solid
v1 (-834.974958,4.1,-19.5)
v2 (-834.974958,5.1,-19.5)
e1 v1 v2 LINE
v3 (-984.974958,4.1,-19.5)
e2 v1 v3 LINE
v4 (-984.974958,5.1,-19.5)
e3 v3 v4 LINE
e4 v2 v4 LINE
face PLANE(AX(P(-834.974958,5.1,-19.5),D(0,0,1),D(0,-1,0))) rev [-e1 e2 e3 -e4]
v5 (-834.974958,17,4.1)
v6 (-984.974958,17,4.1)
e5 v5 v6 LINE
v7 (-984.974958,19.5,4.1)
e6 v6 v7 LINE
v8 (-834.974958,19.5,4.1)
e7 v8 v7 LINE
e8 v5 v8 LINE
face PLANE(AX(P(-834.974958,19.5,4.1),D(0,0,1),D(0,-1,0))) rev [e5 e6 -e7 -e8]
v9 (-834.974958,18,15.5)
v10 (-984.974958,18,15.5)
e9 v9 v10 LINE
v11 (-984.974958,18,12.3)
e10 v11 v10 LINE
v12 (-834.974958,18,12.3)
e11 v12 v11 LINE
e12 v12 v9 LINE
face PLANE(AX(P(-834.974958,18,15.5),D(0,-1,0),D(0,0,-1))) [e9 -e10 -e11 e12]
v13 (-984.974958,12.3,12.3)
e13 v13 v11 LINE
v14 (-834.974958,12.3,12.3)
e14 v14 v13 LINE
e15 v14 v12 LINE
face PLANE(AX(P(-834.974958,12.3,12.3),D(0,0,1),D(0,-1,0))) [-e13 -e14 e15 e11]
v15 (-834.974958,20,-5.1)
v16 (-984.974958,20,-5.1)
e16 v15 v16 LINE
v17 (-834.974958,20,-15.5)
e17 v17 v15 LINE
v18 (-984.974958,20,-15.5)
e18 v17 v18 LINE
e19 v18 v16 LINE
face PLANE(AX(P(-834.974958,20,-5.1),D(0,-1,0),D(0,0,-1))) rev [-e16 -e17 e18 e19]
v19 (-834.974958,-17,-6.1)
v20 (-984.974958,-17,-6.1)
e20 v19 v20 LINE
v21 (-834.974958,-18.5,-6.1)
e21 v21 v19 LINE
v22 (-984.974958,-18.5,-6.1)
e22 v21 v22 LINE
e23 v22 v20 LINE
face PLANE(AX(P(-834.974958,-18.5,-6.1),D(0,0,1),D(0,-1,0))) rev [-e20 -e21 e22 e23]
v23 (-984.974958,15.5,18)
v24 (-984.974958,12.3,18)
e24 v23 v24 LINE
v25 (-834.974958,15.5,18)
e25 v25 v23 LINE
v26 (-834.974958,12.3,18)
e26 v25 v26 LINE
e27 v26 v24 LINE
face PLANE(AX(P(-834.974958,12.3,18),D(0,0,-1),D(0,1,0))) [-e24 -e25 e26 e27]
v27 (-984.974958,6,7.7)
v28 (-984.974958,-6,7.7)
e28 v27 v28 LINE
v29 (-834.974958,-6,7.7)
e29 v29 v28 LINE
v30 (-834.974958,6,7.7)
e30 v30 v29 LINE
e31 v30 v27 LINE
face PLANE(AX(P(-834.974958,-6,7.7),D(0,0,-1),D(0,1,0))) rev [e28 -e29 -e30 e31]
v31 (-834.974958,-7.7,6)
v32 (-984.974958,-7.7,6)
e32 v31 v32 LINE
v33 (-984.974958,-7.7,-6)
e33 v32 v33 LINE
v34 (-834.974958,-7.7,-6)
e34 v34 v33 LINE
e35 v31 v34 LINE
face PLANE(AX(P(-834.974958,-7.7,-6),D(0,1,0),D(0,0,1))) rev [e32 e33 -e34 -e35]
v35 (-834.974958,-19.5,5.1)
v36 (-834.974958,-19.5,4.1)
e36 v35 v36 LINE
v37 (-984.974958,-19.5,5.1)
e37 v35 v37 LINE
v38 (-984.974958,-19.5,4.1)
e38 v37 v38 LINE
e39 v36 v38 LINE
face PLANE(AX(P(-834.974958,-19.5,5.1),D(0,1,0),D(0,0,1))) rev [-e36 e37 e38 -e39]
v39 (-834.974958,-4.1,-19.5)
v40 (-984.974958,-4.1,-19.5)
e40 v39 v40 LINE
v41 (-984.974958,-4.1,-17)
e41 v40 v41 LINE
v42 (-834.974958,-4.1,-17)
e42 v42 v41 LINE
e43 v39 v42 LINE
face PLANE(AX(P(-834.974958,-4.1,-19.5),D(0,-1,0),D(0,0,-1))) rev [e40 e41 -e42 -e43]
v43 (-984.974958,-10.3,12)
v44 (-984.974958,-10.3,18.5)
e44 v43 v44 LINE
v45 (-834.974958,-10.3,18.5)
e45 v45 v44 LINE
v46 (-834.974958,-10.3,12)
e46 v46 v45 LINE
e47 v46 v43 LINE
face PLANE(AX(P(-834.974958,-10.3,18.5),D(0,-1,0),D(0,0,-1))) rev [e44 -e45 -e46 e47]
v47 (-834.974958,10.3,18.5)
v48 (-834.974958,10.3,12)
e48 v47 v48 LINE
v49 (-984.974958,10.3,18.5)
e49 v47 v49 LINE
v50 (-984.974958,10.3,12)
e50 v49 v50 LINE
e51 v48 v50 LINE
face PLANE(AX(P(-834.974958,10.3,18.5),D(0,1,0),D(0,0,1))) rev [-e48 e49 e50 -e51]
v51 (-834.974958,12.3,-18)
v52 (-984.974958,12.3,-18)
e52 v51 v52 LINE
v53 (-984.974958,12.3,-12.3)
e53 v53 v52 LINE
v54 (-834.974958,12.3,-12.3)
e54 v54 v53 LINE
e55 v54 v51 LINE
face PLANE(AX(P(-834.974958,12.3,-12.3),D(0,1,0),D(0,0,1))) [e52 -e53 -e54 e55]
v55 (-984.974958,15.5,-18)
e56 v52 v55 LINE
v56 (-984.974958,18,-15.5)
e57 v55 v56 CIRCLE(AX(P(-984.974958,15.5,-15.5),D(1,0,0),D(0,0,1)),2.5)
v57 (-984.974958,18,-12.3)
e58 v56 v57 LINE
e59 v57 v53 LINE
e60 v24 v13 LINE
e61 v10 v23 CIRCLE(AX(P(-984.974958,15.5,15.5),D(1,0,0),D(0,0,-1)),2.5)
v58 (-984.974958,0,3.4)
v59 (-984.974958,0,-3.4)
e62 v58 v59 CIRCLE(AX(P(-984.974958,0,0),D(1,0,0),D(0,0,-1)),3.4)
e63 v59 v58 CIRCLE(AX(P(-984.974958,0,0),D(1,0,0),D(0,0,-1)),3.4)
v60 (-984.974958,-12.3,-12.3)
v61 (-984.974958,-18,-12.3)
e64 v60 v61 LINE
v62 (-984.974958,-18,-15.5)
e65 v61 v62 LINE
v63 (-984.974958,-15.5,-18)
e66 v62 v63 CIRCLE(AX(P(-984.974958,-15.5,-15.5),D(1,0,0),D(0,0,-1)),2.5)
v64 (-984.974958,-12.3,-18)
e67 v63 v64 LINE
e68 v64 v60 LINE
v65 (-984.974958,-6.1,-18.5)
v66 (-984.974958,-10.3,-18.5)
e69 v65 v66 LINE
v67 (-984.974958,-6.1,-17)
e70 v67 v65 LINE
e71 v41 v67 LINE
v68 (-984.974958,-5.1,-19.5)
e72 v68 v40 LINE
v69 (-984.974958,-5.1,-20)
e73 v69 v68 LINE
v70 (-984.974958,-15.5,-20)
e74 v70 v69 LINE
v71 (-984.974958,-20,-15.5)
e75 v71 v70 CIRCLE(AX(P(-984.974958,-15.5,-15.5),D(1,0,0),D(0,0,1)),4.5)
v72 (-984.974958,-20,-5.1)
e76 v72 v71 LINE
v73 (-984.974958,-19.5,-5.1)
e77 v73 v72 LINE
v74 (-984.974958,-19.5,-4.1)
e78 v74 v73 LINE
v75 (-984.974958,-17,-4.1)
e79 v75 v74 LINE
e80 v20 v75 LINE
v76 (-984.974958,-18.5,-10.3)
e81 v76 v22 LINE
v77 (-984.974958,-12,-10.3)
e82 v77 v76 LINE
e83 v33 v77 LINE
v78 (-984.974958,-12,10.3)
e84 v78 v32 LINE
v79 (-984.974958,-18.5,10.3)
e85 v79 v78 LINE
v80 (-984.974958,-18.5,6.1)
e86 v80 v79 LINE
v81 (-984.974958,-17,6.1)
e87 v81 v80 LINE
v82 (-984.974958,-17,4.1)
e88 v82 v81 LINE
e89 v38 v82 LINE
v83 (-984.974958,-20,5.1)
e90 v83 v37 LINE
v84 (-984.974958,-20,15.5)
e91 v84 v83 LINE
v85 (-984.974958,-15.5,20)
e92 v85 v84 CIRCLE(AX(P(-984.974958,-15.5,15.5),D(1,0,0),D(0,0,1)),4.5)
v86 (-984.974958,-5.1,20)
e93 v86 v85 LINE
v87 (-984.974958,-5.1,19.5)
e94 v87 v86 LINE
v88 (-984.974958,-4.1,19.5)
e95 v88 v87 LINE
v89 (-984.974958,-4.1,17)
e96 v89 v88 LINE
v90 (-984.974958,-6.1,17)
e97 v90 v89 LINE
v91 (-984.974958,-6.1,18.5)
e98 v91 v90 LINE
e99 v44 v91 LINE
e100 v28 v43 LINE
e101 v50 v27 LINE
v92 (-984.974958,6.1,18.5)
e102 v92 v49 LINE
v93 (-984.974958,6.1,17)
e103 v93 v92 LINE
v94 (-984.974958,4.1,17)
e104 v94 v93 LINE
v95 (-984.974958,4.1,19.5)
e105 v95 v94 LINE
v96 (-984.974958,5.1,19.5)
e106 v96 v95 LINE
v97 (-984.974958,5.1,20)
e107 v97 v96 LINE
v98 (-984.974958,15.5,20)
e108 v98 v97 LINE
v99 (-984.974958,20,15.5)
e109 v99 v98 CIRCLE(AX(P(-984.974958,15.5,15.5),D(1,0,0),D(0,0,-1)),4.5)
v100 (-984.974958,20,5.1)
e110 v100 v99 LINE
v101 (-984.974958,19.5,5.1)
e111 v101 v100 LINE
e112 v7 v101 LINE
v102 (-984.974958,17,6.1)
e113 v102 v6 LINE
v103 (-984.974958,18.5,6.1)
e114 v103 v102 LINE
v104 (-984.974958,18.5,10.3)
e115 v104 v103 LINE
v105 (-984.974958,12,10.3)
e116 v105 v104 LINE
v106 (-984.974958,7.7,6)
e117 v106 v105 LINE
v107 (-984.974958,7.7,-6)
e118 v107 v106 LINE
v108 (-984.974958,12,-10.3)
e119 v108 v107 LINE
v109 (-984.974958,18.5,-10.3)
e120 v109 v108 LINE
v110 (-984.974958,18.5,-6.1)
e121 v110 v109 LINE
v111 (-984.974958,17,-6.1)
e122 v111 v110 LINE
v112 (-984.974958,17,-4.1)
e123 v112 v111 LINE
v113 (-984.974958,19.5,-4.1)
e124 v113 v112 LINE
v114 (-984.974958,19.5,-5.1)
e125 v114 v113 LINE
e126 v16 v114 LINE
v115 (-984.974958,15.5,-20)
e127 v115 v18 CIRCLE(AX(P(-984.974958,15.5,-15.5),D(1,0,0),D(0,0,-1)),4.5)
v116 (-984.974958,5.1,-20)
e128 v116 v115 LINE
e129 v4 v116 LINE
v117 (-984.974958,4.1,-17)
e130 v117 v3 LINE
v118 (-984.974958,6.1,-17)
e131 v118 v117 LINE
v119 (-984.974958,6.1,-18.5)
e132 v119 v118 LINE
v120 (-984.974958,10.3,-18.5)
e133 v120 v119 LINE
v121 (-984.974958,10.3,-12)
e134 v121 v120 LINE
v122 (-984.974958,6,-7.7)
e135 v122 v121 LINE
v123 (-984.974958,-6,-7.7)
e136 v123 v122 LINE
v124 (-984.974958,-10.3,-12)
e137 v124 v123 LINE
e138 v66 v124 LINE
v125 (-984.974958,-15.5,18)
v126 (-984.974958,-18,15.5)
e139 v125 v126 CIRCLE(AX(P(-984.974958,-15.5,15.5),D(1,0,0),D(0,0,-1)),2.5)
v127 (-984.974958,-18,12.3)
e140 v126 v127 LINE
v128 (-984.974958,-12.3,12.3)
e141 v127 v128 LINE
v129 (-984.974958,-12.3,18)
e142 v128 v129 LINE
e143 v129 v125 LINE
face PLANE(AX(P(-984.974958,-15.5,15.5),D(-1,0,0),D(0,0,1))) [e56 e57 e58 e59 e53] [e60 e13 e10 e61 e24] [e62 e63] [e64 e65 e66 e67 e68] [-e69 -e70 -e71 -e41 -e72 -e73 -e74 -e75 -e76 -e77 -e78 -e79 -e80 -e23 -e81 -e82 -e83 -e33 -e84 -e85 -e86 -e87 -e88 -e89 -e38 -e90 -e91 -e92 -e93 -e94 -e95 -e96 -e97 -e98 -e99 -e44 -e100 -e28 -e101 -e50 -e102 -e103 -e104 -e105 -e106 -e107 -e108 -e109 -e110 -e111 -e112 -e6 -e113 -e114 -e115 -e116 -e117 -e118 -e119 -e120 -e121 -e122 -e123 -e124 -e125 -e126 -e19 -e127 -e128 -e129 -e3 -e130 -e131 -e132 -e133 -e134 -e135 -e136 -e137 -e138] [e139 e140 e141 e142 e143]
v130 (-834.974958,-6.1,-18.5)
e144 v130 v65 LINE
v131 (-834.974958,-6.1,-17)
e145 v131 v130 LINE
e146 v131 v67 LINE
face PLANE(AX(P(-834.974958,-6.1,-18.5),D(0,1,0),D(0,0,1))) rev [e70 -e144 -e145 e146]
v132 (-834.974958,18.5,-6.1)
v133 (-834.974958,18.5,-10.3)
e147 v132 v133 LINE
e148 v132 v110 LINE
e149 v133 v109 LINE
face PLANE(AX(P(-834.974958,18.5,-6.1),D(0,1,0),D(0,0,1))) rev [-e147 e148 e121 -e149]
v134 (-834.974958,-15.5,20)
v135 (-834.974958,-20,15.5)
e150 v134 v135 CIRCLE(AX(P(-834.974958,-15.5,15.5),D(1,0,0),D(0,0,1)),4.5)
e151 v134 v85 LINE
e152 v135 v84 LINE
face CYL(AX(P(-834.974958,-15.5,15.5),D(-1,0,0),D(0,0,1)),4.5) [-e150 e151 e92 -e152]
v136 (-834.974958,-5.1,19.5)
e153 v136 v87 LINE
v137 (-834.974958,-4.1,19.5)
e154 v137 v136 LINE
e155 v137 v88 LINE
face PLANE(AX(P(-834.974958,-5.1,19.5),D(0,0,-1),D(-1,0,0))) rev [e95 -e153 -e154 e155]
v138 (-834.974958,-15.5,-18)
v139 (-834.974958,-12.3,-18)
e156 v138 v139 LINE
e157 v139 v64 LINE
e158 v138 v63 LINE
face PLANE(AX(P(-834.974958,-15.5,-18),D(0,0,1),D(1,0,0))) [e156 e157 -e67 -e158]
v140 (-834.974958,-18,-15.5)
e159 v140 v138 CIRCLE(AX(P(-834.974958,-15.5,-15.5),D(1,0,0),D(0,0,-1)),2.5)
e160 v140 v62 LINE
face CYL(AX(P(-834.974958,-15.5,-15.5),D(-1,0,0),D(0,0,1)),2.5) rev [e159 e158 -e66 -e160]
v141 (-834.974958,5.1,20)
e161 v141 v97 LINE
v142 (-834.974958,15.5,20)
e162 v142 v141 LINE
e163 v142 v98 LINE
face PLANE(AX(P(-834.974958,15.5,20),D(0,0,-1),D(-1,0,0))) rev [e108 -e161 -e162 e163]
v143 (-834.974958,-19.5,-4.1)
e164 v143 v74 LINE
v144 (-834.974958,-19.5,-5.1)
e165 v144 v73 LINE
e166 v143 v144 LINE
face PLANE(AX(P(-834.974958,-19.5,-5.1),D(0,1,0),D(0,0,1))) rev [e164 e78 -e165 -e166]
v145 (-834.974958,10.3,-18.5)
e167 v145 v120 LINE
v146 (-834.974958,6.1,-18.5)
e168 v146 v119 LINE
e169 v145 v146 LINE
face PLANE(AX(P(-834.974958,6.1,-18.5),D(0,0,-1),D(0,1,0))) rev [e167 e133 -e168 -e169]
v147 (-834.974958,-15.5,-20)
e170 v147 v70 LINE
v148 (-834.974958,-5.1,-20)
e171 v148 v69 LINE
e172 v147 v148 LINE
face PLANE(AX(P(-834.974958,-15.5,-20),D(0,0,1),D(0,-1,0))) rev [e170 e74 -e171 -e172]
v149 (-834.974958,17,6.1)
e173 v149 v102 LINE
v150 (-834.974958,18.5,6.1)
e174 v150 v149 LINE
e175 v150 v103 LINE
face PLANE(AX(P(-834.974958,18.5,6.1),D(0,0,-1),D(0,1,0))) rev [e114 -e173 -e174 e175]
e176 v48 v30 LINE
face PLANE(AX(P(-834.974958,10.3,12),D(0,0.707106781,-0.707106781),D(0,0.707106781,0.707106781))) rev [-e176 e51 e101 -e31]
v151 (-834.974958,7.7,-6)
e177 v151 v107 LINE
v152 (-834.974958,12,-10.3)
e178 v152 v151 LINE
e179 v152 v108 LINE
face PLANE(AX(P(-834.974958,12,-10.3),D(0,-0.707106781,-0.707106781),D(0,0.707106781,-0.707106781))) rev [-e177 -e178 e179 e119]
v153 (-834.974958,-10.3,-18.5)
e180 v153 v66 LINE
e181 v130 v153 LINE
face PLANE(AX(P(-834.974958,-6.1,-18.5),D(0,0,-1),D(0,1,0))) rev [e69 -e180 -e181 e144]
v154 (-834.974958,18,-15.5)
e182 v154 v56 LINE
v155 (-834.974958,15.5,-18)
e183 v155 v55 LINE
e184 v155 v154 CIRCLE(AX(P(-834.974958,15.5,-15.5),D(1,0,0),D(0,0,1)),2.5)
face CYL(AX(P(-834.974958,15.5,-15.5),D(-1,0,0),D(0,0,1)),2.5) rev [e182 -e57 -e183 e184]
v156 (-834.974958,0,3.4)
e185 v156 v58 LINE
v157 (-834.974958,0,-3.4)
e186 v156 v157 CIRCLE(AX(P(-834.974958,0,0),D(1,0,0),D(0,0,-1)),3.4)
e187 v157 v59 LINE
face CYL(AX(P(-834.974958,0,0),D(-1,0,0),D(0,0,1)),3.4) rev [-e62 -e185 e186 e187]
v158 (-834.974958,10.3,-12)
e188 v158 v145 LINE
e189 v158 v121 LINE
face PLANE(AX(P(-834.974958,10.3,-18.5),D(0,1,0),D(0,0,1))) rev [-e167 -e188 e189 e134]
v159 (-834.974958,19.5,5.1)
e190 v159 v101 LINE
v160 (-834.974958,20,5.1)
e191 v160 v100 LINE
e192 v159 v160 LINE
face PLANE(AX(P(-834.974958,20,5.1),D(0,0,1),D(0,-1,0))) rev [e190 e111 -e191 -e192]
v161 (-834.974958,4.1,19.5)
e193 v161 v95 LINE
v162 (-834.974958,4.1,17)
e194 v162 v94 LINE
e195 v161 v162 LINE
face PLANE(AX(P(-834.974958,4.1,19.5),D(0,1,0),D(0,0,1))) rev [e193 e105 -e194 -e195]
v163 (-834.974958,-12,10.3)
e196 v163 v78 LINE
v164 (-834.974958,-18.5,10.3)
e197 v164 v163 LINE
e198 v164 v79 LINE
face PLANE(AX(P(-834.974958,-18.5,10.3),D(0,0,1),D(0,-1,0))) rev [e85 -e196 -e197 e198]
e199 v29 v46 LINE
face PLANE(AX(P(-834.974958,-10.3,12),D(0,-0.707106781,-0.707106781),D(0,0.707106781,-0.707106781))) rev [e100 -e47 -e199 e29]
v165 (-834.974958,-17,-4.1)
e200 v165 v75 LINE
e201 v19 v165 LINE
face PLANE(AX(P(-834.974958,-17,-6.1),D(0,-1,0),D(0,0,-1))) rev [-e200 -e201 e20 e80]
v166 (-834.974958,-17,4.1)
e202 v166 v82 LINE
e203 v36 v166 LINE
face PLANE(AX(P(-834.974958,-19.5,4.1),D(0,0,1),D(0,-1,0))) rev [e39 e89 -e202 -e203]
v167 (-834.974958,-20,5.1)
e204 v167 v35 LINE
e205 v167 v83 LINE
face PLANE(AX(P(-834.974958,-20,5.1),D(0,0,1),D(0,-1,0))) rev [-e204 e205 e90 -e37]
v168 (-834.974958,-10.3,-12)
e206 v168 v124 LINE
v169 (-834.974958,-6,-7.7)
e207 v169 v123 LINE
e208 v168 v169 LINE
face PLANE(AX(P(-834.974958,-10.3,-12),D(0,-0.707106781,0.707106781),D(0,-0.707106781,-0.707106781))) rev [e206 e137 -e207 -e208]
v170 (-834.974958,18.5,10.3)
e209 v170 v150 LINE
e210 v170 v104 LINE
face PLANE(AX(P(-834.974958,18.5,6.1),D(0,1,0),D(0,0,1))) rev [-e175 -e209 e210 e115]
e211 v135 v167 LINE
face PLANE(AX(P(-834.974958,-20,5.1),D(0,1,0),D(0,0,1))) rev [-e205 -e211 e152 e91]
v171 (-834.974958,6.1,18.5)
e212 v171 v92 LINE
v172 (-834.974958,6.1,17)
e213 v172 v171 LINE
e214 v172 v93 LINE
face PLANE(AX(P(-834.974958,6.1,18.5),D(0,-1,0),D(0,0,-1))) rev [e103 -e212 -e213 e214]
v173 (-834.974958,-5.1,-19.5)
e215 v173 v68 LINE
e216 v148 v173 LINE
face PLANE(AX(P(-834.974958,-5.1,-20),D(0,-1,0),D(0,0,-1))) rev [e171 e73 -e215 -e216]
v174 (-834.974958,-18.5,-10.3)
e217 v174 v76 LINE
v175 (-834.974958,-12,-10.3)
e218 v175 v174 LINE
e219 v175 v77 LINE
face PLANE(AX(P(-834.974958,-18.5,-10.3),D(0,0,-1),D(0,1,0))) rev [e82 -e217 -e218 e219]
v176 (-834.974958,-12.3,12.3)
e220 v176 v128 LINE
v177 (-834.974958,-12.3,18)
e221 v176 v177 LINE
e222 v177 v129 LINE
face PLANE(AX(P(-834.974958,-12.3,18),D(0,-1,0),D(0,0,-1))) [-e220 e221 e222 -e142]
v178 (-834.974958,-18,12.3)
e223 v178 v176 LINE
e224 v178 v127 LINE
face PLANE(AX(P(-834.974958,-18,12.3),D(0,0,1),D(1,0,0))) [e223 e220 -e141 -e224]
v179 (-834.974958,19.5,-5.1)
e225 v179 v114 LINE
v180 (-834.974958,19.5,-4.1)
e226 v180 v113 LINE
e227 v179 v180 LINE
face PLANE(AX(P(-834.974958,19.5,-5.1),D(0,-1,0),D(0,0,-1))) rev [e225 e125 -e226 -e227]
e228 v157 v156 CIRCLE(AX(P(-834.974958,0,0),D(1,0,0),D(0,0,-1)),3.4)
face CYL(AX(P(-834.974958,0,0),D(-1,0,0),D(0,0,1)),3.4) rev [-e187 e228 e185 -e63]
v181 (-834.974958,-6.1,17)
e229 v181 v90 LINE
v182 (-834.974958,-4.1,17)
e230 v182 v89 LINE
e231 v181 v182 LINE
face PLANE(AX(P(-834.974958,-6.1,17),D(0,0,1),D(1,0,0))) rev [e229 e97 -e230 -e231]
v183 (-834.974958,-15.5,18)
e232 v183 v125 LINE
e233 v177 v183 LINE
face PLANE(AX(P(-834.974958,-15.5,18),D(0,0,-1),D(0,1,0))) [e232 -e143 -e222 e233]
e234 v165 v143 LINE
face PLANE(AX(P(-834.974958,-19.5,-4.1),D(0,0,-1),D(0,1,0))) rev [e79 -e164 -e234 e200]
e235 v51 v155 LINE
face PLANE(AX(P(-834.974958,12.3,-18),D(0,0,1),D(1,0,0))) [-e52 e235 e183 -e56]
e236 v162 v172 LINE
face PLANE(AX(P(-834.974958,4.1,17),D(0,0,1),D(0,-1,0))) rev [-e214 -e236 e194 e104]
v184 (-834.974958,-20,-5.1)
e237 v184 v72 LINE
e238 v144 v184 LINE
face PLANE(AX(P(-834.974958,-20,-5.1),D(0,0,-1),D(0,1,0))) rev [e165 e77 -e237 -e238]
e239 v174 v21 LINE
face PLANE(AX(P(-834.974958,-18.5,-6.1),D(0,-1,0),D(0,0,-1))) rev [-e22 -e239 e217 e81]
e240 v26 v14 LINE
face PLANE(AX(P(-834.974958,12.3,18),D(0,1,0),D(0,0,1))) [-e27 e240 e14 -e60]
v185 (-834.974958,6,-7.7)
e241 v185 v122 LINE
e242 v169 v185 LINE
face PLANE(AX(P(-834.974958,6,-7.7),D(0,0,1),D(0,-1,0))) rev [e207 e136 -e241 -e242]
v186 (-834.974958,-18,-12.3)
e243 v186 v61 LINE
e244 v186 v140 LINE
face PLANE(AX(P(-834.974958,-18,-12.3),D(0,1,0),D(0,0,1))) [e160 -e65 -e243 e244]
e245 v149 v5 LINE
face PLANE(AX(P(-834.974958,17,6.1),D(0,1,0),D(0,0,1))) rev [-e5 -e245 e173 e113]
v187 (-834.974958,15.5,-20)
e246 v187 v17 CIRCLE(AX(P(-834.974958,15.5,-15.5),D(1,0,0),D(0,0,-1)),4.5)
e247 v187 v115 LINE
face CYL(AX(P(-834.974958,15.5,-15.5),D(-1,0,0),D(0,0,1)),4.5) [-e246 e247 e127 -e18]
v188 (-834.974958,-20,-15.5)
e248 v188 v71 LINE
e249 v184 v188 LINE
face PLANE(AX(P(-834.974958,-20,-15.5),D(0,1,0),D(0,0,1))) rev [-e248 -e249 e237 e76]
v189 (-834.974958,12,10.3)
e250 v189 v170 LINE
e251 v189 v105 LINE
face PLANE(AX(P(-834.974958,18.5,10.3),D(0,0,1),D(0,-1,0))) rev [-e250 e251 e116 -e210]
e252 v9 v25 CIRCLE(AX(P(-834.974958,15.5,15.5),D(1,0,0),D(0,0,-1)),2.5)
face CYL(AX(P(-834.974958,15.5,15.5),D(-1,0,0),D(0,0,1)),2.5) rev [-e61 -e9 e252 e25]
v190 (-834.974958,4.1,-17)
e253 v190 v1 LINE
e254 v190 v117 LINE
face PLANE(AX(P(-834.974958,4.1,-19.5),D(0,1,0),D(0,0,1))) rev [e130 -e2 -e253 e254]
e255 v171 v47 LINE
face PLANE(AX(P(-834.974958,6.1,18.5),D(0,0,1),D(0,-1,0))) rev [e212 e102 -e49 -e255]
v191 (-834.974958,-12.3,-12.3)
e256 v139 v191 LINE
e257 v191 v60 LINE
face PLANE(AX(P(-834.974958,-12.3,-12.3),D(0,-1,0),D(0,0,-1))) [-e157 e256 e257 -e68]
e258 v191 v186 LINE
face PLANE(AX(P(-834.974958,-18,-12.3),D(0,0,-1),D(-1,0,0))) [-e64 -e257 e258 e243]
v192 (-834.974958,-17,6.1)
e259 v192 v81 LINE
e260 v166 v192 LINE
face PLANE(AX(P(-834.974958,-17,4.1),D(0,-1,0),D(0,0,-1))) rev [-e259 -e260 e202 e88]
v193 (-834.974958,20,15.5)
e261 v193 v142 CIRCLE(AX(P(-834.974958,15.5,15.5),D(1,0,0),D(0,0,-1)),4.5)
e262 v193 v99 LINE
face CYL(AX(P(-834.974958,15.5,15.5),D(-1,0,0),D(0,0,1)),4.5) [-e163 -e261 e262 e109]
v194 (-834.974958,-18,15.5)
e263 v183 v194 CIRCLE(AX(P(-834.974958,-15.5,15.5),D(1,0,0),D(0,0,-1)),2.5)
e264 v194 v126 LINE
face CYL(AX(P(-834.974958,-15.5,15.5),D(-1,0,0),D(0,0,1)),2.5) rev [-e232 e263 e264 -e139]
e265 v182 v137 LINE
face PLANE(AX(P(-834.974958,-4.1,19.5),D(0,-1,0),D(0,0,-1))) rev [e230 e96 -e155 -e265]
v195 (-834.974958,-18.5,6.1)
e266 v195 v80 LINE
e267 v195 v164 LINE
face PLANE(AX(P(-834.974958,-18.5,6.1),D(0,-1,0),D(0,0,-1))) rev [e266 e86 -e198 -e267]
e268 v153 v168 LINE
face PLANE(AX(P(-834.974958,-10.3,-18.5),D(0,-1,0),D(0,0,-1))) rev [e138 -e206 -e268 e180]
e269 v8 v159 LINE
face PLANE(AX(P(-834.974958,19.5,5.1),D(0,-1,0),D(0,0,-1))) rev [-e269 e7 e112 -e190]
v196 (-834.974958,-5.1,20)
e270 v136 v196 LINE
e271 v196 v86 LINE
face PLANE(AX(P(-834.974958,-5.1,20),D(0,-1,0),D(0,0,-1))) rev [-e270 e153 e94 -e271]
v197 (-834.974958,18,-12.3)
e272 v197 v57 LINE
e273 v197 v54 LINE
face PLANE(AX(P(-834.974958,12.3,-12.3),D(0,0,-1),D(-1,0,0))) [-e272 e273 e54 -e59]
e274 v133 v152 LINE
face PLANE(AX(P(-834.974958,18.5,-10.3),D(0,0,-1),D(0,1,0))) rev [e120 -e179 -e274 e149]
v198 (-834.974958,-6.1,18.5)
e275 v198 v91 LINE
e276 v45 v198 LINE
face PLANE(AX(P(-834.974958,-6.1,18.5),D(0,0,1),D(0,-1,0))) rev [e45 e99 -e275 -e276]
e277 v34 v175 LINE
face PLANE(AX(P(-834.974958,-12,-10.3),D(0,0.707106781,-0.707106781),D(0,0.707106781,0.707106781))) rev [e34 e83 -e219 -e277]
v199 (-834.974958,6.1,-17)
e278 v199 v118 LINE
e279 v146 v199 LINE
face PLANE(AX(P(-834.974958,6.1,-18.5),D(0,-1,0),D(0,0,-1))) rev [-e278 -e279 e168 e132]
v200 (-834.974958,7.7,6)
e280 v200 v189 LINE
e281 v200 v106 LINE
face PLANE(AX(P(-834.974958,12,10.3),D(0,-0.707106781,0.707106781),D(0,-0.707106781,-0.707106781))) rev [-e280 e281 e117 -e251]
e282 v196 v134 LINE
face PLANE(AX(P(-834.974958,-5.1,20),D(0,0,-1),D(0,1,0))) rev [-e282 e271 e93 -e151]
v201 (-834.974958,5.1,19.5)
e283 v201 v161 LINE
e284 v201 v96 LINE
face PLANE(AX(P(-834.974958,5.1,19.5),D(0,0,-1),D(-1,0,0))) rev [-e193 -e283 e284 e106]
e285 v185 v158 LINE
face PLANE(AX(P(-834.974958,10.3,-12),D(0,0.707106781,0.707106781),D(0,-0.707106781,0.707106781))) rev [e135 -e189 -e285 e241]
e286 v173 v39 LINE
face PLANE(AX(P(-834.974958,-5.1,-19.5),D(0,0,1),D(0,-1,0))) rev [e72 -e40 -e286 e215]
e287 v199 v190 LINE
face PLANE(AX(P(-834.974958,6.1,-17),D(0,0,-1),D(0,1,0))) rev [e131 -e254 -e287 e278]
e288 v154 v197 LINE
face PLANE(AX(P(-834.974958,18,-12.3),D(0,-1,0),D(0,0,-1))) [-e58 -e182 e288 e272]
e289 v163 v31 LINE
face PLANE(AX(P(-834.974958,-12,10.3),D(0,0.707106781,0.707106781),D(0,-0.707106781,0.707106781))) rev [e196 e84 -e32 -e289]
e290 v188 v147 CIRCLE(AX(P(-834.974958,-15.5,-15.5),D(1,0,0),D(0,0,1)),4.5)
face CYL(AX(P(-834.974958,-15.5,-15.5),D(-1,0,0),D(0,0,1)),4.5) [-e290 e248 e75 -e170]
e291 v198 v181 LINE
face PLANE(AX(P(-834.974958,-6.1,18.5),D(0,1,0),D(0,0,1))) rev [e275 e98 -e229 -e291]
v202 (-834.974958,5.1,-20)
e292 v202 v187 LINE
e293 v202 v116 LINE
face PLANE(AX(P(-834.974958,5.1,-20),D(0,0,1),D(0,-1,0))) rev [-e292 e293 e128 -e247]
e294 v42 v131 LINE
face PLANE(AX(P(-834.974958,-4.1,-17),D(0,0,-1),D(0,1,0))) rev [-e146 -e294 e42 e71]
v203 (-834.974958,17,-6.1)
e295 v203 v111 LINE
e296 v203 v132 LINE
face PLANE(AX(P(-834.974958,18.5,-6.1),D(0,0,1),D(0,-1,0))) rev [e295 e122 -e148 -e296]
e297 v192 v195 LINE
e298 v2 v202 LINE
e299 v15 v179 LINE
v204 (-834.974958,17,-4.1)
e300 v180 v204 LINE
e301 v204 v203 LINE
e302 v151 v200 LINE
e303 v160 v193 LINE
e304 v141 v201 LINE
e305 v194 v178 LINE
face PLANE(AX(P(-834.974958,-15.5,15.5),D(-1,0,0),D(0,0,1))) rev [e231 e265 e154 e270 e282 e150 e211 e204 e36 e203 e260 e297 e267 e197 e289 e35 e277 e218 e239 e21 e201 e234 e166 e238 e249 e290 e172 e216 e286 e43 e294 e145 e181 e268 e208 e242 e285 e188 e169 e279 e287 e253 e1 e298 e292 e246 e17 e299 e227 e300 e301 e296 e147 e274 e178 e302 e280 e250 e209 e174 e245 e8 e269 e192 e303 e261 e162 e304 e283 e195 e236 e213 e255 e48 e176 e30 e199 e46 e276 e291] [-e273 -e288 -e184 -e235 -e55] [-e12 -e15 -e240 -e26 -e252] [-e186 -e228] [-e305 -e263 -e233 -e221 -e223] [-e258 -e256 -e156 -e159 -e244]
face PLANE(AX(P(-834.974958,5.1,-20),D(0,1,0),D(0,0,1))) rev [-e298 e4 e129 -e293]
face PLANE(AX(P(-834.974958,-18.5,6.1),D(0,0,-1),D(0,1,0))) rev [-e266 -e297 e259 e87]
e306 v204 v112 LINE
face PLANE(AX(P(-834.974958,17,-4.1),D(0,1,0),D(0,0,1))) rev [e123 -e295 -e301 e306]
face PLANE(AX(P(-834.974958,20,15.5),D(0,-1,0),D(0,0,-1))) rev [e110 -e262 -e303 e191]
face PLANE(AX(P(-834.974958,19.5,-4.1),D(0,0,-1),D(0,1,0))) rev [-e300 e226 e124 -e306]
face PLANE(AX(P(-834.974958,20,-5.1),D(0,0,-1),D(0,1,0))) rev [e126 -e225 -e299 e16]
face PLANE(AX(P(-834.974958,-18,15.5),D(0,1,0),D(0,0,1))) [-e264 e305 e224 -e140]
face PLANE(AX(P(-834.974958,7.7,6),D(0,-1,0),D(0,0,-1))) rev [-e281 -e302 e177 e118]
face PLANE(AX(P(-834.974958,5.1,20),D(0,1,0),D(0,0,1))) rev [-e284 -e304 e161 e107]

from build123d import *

# Parameters (mm, degrees)
SKETCH1_R                                 = 3.4
ALUMINIUM_PROFILE_40_X_40B_X_R4_5_1_DEPTH = 150


with BuildPart() as part:
    # Sketch1 → Aluminium profile 40 X 40B X R4.5(1) (new body)
    with BuildSketch(Plane.YZ.offset(-984.974958264)):
        with BuildLine():
            Line((-5.1, 20), (-5.1, 19.5))
            Line((-5.1, 19.5), (-4.1, 19.5))
            Line((-4.1, 19.5), (-4.1, 17))
            Line((-4.1, 17), (-6.1, 17))
            Line((-6.1, 17), (-6.1, 18.5))
            Line((-6.1, 18.5), (-10.3, 18.5))
            Line((-10.3, 18.5), (-10.3, 12))
            Line((-10.3, 12), (-6, 7.7))
            Line((-6, 7.7), (6, 7.7))
            Line((6, 7.7), (10.3, 12))
            Line((10.3, 12), (10.3, 18.5))
            Line((10.3, 18.5), (6.1, 18.5))
            Line((6.1, 18.5), (6.1, 17))
            Line((6.1, 17), (4.1, 17))
            Line((4.1, 17), (4.1, 19.5))
            Line((4.1, 19.5), (5.1, 19.5))
            Line((5.1, 19.5), (5.1, 20))
            Line((5.1, 20), (15.5, 20))
            ThreePointArc((15.5, 20), (18.681980515, 18.681980515), (20, 15.5))
            Line((20, 15.5), (20, 5.1))
            Line((20, 5.1), (19.5, 5.1))
            Line((19.5, 5.1), (19.5, 4.1))
            Line((19.5, 4.1), (17, 4.1))
            Line((17, 4.1), (17, 6.1))
            Line((17, 6.1), (18.5, 6.1))
            Line((18.5, 6.1), (18.5, 10.3))
            Line((18.5, 10.3), (12, 10.3))
            Line((12, 10.3), (7.7, 6))
            Line((7.7, 6), (7.7, -6))
            Line((7.7, -6), (12, -10.3))
            Line((12, -10.3), (18.5, -10.3))
            Line((18.5, -10.3), (18.5, -6.1))
            Line((18.5, -6.1), (17, -6.1))
            Line((17, -6.1), (17, -4.1))
            Line((17, -4.1), (19.5, -4.1))
            Line((19.5, -4.1), (19.5, -5.1))
            Line((19.5, -5.1), (20, -5.1))
            Line((20, -5.1), (20, -15.5))
            ThreePointArc((20, -15.5), (18.681980515, -18.681980515), (15.5, -20))
            Line((15.5, -20), (5.1, -20))
            Line((5.1, -20), (5.1, -19.5))
            Line((5.1, -19.5), (4.1, -19.5))
            Line((4.1, -19.5), (4.1, -17))
            Line((4.1, -17), (6.1, -17))
            Line((6.1, -17), (6.1, -18.5))
            Line((6.1, -18.5), (10.3, -18.5))
            Line((10.3, -18.5), (10.3, -12))
            Line((10.3, -12), (6, -7.7))
            Line((6, -7.7), (-6, -7.7))
            Line((-6, -7.7), (-10.3, -12))
            Line((-10.3, -12), (-10.3, -18.5))
            Line((-10.3, -18.5), (-6.1, -18.5))
            Line((-6.1, -18.5), (-6.1, -17))
            Line((-6.1, -17), (-4.1, -17))
            Line((-4.1, -17), (-4.1, -19.5))
            Line((-4.1, -19.5), (-5.1, -19.5))
            Line((-5.1, -19.5), (-5.1, -20))
            Line((-5.1, -20), (-15.5, -20))
            ThreePointArc((-15.5, -20), (-18.681980515, -18.681980515), (-20, -15.5))
            Line((-20, -15.5), (-20, -5.1))
            Line((-20, -5.1), (-19.5, -5.1))
            Line((-19.5, -5.1), (-19.5, -4.1))
            Line((-19.5, -4.1), (-17, -4.1))
            Line((-17, -4.1), (-17, -6.1))
            Line((-17, -6.1), (-18.5, -6.1))
            Line((-18.5, -6.1), (-18.5, -10.3))
            Line((-18.5, -10.3), (-12, -10.3))
            Line((-12, -10.3), (-7.7, -6))
            Line((-7.7, -6), (-7.7, 6))
            Line((-7.7, 6), (-12, 10.3))
            Line((-12, 10.3), (-18.5, 10.3))
            Line((-18.5, 10.3), (-18.5, 6.1))
            Line((-18.5, 6.1), (-17, 6.1))
            Line((-17, 6.1), (-17, 4.1))
            Line((-17, 4.1), (-19.5, 4.1))
            Line((-19.5, 4.1), (-19.5, 5.1))
            Line((-19.5, 5.1), (-20, 5.1))
            Line((-20, 5.1), (-20, 15.5))
            ThreePointArc((-20, 15.5), (-18.681980515, 18.681980515), (-15.5, 20))
            Line((-15.5, 20), (-5.1, 20))
        make_face()
        Circle(SKETCH1_R, mode=Mode.SUBTRACT)
        with BuildLine():
            Line((12.3, 18), (15.5, 18))
            ThreePointArc((15.5, 18), (17.267766953, 17.267766953), (18, 15.5))
            Line((18, 15.5), (18, 12.3))
            Line((18, 12.3), (12.3, 12.3))
            Line((12.3, 12.3), (12.3, 18))
        make_face(mode=Mode.SUBTRACT)
        with BuildLine():
            Line((-15.5, 18), (-12.3, 18))
            Line((-12.3, 18), (-12.3, 12.3))
            Line((-12.3, 12.3), (-18, 12.3))
            Line((-18, 12.3), (-18, 15.5))
            ThreePointArc((-18, 15.5), (-17.267766953, 17.267766953), (-15.5, 18))
        make_face(mode=Mode.SUBTRACT)
        with BuildLine():
            Line((-18, -12.3), (-12.3, -12.3))
            Line((-12.3, -12.3), (-12.3, -18))
            Line((-12.3, -18), (-15.5, -18))
            ThreePointArc((-15.5, -18), (-17.267766953, -17.267766953), (-18, -15.5))
            Line((-18, -15.5), (-18, -12.3))
        make_face(mode=Mode.SUBTRACT)
        with BuildLine():
            Line((12.3, -12.3), (18, -12.3))
            Line((18, -12.3), (18, -15.5))
            ThreePointArc((18, -15.5), (17.267766953, -17.267766953), (15.5, -18))
            Line((15.5, -18), (12.3, -18))
            Line((12.3, -18), (12.3, -12.3))
        make_face(mode=Mode.SUBTRACT)
    extrude(amount=ALUMINIUM_PROFILE_40_X_40B_X_R4_5_1_DEPTH)


solid = part.part
